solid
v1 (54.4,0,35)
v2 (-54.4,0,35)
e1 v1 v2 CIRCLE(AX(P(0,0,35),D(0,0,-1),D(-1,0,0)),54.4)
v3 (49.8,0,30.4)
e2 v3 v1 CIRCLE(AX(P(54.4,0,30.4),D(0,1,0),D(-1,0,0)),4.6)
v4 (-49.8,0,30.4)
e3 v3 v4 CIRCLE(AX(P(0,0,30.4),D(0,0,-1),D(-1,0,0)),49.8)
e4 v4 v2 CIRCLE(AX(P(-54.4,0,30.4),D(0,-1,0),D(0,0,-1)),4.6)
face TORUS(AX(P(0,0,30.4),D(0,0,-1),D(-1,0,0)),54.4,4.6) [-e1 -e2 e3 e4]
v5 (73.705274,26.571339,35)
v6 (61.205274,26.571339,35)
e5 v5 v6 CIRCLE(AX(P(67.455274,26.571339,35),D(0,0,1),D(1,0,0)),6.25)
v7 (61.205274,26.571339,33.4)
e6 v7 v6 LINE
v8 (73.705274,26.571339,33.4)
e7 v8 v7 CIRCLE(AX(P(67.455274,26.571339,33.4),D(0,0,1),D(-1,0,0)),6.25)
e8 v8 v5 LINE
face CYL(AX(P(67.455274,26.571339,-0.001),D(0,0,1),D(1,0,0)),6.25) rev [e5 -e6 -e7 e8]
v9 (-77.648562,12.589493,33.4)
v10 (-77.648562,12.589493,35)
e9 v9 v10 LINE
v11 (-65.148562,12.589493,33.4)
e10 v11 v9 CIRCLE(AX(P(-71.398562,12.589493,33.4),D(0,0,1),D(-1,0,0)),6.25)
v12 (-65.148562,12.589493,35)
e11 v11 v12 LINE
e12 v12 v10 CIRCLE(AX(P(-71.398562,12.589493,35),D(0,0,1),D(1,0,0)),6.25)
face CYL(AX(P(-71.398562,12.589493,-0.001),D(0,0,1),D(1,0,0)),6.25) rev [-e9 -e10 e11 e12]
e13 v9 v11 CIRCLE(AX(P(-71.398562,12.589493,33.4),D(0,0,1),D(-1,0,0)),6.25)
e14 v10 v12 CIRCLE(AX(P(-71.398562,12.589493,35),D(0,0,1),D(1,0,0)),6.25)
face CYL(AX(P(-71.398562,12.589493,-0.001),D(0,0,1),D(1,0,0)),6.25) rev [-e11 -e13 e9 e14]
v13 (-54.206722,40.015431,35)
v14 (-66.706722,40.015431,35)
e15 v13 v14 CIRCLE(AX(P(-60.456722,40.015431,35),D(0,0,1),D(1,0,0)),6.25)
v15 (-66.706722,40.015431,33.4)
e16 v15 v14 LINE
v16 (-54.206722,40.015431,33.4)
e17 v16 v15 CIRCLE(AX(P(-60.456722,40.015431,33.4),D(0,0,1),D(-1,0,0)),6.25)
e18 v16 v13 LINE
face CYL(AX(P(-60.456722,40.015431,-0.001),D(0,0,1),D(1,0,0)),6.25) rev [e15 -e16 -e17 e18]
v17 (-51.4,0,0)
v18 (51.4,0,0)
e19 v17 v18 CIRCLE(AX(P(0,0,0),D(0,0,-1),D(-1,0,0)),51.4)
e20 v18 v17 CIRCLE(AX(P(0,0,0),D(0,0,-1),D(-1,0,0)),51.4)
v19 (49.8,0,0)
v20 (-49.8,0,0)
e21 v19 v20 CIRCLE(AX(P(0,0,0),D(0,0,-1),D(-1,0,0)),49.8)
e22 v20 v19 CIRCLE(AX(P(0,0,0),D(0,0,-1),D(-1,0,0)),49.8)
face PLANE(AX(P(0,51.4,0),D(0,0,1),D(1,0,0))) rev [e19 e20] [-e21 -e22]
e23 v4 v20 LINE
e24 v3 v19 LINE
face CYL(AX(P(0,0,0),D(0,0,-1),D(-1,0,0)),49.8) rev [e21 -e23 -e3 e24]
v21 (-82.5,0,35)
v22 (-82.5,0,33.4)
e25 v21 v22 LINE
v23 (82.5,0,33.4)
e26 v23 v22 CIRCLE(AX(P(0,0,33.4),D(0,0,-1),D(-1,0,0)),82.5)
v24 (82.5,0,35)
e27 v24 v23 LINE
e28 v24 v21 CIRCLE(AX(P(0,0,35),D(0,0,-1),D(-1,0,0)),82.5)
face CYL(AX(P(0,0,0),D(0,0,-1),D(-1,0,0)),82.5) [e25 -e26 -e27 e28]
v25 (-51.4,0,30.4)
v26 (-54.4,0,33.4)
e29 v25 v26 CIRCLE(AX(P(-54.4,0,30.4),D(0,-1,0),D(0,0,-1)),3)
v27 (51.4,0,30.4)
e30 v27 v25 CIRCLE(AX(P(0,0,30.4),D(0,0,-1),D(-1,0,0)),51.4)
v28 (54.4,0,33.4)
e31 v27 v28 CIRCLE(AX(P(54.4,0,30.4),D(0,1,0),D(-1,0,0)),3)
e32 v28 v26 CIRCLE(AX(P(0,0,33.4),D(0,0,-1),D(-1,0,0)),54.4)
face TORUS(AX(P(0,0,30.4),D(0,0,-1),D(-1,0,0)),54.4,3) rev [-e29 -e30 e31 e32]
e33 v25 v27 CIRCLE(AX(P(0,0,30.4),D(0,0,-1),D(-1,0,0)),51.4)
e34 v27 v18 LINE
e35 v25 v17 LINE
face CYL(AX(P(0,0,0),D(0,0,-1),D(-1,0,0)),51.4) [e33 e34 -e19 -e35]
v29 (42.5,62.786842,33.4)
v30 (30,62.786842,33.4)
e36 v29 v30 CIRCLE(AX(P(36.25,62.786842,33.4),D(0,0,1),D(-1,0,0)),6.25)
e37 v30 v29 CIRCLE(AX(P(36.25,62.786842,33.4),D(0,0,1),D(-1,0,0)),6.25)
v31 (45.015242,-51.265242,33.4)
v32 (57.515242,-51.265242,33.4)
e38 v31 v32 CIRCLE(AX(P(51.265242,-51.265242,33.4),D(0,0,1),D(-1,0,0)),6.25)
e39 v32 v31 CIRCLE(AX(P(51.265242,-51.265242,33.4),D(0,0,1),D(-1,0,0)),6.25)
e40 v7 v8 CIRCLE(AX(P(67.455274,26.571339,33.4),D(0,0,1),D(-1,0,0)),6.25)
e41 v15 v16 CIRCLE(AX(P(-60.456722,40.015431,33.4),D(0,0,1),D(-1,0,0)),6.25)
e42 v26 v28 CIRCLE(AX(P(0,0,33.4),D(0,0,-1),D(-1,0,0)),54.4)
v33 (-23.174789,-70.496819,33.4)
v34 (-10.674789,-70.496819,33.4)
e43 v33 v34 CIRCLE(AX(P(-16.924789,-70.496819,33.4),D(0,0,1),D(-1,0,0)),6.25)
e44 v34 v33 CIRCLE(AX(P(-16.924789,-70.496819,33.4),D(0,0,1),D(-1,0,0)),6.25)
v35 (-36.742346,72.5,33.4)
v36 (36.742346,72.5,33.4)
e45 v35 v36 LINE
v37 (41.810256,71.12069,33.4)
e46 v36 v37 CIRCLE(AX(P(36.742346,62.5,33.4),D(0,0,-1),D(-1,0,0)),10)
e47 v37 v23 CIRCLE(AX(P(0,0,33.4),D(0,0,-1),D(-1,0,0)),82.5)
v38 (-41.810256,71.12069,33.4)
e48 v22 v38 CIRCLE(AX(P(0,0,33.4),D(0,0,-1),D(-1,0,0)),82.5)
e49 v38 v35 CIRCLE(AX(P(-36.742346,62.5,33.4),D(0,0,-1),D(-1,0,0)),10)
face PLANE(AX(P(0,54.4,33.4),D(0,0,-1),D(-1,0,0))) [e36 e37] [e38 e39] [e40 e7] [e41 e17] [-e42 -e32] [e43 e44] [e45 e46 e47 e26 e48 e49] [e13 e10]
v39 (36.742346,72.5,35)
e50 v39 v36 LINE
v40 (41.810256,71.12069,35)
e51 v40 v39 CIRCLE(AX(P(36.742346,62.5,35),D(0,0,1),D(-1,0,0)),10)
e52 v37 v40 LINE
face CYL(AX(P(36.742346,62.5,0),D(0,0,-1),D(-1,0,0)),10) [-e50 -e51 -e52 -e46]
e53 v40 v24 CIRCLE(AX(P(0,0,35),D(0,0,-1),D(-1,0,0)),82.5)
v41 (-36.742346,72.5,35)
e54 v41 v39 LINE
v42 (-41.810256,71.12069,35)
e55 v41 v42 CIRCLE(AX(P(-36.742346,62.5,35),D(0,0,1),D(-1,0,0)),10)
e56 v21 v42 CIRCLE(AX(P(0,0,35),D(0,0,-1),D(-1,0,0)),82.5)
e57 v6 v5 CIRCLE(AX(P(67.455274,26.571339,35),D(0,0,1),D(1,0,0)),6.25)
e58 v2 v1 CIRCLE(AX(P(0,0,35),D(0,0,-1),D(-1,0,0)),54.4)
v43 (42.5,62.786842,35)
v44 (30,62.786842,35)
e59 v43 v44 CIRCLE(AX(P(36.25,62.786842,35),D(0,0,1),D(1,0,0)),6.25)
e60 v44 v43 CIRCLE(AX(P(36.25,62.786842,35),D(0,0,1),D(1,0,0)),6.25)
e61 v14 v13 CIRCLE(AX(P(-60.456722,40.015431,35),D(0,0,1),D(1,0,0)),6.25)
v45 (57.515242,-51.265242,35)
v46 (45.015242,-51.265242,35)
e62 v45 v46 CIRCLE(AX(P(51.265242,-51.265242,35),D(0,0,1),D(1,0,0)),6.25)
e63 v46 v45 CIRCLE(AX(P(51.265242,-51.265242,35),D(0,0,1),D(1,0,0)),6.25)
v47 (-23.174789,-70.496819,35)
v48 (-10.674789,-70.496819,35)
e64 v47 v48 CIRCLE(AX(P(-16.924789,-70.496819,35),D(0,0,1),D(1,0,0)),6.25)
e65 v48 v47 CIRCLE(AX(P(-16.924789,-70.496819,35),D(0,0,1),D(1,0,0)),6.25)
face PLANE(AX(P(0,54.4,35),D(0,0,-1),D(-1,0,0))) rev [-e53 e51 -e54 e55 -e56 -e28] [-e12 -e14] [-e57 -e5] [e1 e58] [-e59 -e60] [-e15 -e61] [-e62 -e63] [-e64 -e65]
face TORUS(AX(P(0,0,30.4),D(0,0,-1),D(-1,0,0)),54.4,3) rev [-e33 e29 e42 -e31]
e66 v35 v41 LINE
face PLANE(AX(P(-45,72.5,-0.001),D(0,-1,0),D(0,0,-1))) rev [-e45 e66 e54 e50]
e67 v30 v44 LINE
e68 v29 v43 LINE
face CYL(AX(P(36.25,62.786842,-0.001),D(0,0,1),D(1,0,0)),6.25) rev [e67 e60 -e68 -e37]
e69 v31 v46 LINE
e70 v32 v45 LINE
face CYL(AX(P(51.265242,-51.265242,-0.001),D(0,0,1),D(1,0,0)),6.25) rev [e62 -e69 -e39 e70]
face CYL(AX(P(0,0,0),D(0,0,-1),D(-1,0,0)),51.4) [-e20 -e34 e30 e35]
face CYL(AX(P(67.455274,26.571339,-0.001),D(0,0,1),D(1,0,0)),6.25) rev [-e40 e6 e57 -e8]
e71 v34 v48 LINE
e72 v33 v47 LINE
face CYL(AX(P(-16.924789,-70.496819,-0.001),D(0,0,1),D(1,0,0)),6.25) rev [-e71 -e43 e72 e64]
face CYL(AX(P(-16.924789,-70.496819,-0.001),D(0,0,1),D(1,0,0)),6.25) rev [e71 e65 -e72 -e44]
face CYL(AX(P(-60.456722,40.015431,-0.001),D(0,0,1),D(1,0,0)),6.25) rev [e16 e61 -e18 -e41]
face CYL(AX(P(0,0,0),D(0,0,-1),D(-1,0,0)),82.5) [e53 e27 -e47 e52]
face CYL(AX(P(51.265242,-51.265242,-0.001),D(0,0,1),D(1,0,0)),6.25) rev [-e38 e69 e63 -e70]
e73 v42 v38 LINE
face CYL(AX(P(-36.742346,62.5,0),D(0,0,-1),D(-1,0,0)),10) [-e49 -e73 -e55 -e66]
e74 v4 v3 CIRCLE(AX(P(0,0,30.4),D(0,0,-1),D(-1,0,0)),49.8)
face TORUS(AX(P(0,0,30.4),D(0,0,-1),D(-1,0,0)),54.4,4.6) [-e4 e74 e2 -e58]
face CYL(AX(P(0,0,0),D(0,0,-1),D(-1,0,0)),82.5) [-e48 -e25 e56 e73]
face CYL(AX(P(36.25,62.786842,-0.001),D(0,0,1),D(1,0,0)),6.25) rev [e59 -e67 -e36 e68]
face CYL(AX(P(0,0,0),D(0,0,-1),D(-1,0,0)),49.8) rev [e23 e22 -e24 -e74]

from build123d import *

# Parameters (mm, degrees)
CUT_EXTRUDE1_REACH = 123.809
SKETCH2_R          = 6.25
SKETCH2_W          = 90
SKETCH2_H          = 12
FILLET1_R          = 10


with BuildPart() as part:
    # Sketch1 → Revolve-Thin2 (revolve)
    with BuildSketch(Plane(origin=(0, 0, 0), x_dir=(0, 0, -1), z_dir=(1, 0, 0)), mode=Mode.PRIVATE) as revolve_thin2_sk:
        with BuildLine():
            Line((0, 49.8), (-30.4, 49.8))
            ThreePointArc((-30.4, 49.8), (-33.652691193, 51.147308807), (-35, 54.4))
            Line((-35, 54.4), (-35, 82.5))
            Line((-35, 82.5), (-33.4, 82.5))
            Line((-33.4, 82.5), (-33.4, 54.4))
            ThreePointArc((-33.4, 54.4), (-32.521320344, 52.278679656), (-30.4, 51.4))
            Line((-30.4, 51.4), (0, 51.4))
            Line((0, 51.4), (0, 49.8))
        make_face()
    revolve(revolve_thin2_sk.sketch.rotate(Axis((0, 0, 0), (0, 0, 1)), 90), axis=Axis((0, 0, 0), (0, 0, 1)))

    # Sketch2 → Cut-Extrude1 (cut, up to next)
    with BuildSketch(Plane.XY.offset(35), mode=Mode.PRIVATE) as cut_extrude1_sk1:
        with Locations((-60.4567221, 40.015431435)):
            Circle(SKETCH2_R)
    cut_extrude1_tool1 = extrude(cut_extrude1_sk1.sketch, amount=-CUT_EXTRUDE1_REACH, mode=Mode.PRIVATE) & part.part
    # Sketch2 → Cut-Extrude1 (cut, up to next)
    with BuildSketch(Plane.XY.offset(35), mode=Mode.PRIVATE) as cut_extrude1_sk2:
        with Locations((36.25, 62.786841774)):
            Circle(SKETCH2_R)
    cut_extrude1_tool2 = extrude(cut_extrude1_sk2.sketch, amount=-CUT_EXTRUDE1_REACH, mode=Mode.PRIVATE) & part.part
    # Sketch2 → Cut-Extrude1 (cut, up to next)
    with BuildSketch(Plane.XY.offset(35), mode=Mode.PRIVATE) as cut_extrude1_sk3:
        with Locations((67.455273679, 26.571338938)):
            Circle(SKETCH2_R)
    cut_extrude1_tool3 = extrude(cut_extrude1_sk3.sketch, amount=-CUT_EXTRUDE1_REACH, mode=Mode.PRIVATE) & part.part
    # Sketch2 → Cut-Extrude1 (cut, up to next)
    with BuildSketch(Plane.XY.offset(35), mode=Mode.PRIVATE) as cut_extrude1_sk4:
        with Locations((51.265241636, -51.265241636)):
            Circle(SKETCH2_R)
    cut_extrude1_tool4 = extrude(cut_extrude1_sk4.sketch, amount=-CUT_EXTRUDE1_REACH, mode=Mode.PRIVATE) & part.part
    # Sketch2 → Cut-Extrude1 (cut, up to next)
    with BuildSketch(Plane.XY.offset(35), mode=Mode.PRIVATE) as cut_extrude1_sk5:
        with Locations((-16.92478888, -70.496819229)):
            Circle(SKETCH2_R)
    cut_extrude1_tool5 = extrude(cut_extrude1_sk5.sketch, amount=-CUT_EXTRUDE1_REACH, mode=Mode.PRIVATE) & part.part
    # Sketch2 → Cut-Extrude1 (cut, up to next)
    with BuildSketch(Plane.XY.offset(35), mode=Mode.PRIVATE) as cut_extrude1_sk6:
        with Locations((-71.398562093, 12.589492881)):
            Circle(SKETCH2_R)
    cut_extrude1_tool6 = extrude(cut_extrude1_sk6.sketch, amount=-CUT_EXTRUDE1_REACH, mode=Mode.PRIVATE) & part.part
    # Sketch2 → Cut-Extrude1 (cut, up to next)
    with BuildSketch(Plane.XY.offset(35), mode=Mode.PRIVATE) as cut_extrude1_sk7:
        with Locations((0, 78.5)):
            Rectangle(SKETCH2_W, SKETCH2_H)
    cut_extrude1_tool7 = extrude(cut_extrude1_sk7.sketch, amount=-CUT_EXTRUDE1_REACH, mode=Mode.PRIVATE) & part.part
    add(cut_extrude1_tool1.solids().sort_by_distance((-60.456722, 40.015431, 35))[0], mode=Mode.SUBTRACT)
    add(cut_extrude1_tool2.solids().sort_by_distance((36.25, 62.786842, 35))[0], mode=Mode.SUBTRACT)
    add(cut_extrude1_tool3.solids().sort_by_distance((67.455274, 26.571339, 35))[0], mode=Mode.SUBTRACT)
    add(cut_extrude1_tool4.solids().sort_by_distance((51.265242, -51.265242, 35))[0], mode=Mode.SUBTRACT)
    add(cut_extrude1_tool5.solids().sort_by_distance((-16.924789, -70.496819, 35))[0], mode=Mode.SUBTRACT)
    add(cut_extrude1_tool6.solids().sort_by_distance((-71.398562, 12.589493, 35))[0], mode=Mode.SUBTRACT)
    add(cut_extrude1_tool7.solids().sort_by_distance((0, 78.5, 35))[0], mode=Mode.SUBTRACT)

    # Fillet1
    fillet1_edges = [part.edges().sort_by_distance(p)[0] for p in [
        (-39.37003937, 72.5, 34.2),
        (39.37003937, 72.5, 34.2),
    ]]
    fillet(fillet1_edges, radius=FILLET1_R)


solid = part.part
